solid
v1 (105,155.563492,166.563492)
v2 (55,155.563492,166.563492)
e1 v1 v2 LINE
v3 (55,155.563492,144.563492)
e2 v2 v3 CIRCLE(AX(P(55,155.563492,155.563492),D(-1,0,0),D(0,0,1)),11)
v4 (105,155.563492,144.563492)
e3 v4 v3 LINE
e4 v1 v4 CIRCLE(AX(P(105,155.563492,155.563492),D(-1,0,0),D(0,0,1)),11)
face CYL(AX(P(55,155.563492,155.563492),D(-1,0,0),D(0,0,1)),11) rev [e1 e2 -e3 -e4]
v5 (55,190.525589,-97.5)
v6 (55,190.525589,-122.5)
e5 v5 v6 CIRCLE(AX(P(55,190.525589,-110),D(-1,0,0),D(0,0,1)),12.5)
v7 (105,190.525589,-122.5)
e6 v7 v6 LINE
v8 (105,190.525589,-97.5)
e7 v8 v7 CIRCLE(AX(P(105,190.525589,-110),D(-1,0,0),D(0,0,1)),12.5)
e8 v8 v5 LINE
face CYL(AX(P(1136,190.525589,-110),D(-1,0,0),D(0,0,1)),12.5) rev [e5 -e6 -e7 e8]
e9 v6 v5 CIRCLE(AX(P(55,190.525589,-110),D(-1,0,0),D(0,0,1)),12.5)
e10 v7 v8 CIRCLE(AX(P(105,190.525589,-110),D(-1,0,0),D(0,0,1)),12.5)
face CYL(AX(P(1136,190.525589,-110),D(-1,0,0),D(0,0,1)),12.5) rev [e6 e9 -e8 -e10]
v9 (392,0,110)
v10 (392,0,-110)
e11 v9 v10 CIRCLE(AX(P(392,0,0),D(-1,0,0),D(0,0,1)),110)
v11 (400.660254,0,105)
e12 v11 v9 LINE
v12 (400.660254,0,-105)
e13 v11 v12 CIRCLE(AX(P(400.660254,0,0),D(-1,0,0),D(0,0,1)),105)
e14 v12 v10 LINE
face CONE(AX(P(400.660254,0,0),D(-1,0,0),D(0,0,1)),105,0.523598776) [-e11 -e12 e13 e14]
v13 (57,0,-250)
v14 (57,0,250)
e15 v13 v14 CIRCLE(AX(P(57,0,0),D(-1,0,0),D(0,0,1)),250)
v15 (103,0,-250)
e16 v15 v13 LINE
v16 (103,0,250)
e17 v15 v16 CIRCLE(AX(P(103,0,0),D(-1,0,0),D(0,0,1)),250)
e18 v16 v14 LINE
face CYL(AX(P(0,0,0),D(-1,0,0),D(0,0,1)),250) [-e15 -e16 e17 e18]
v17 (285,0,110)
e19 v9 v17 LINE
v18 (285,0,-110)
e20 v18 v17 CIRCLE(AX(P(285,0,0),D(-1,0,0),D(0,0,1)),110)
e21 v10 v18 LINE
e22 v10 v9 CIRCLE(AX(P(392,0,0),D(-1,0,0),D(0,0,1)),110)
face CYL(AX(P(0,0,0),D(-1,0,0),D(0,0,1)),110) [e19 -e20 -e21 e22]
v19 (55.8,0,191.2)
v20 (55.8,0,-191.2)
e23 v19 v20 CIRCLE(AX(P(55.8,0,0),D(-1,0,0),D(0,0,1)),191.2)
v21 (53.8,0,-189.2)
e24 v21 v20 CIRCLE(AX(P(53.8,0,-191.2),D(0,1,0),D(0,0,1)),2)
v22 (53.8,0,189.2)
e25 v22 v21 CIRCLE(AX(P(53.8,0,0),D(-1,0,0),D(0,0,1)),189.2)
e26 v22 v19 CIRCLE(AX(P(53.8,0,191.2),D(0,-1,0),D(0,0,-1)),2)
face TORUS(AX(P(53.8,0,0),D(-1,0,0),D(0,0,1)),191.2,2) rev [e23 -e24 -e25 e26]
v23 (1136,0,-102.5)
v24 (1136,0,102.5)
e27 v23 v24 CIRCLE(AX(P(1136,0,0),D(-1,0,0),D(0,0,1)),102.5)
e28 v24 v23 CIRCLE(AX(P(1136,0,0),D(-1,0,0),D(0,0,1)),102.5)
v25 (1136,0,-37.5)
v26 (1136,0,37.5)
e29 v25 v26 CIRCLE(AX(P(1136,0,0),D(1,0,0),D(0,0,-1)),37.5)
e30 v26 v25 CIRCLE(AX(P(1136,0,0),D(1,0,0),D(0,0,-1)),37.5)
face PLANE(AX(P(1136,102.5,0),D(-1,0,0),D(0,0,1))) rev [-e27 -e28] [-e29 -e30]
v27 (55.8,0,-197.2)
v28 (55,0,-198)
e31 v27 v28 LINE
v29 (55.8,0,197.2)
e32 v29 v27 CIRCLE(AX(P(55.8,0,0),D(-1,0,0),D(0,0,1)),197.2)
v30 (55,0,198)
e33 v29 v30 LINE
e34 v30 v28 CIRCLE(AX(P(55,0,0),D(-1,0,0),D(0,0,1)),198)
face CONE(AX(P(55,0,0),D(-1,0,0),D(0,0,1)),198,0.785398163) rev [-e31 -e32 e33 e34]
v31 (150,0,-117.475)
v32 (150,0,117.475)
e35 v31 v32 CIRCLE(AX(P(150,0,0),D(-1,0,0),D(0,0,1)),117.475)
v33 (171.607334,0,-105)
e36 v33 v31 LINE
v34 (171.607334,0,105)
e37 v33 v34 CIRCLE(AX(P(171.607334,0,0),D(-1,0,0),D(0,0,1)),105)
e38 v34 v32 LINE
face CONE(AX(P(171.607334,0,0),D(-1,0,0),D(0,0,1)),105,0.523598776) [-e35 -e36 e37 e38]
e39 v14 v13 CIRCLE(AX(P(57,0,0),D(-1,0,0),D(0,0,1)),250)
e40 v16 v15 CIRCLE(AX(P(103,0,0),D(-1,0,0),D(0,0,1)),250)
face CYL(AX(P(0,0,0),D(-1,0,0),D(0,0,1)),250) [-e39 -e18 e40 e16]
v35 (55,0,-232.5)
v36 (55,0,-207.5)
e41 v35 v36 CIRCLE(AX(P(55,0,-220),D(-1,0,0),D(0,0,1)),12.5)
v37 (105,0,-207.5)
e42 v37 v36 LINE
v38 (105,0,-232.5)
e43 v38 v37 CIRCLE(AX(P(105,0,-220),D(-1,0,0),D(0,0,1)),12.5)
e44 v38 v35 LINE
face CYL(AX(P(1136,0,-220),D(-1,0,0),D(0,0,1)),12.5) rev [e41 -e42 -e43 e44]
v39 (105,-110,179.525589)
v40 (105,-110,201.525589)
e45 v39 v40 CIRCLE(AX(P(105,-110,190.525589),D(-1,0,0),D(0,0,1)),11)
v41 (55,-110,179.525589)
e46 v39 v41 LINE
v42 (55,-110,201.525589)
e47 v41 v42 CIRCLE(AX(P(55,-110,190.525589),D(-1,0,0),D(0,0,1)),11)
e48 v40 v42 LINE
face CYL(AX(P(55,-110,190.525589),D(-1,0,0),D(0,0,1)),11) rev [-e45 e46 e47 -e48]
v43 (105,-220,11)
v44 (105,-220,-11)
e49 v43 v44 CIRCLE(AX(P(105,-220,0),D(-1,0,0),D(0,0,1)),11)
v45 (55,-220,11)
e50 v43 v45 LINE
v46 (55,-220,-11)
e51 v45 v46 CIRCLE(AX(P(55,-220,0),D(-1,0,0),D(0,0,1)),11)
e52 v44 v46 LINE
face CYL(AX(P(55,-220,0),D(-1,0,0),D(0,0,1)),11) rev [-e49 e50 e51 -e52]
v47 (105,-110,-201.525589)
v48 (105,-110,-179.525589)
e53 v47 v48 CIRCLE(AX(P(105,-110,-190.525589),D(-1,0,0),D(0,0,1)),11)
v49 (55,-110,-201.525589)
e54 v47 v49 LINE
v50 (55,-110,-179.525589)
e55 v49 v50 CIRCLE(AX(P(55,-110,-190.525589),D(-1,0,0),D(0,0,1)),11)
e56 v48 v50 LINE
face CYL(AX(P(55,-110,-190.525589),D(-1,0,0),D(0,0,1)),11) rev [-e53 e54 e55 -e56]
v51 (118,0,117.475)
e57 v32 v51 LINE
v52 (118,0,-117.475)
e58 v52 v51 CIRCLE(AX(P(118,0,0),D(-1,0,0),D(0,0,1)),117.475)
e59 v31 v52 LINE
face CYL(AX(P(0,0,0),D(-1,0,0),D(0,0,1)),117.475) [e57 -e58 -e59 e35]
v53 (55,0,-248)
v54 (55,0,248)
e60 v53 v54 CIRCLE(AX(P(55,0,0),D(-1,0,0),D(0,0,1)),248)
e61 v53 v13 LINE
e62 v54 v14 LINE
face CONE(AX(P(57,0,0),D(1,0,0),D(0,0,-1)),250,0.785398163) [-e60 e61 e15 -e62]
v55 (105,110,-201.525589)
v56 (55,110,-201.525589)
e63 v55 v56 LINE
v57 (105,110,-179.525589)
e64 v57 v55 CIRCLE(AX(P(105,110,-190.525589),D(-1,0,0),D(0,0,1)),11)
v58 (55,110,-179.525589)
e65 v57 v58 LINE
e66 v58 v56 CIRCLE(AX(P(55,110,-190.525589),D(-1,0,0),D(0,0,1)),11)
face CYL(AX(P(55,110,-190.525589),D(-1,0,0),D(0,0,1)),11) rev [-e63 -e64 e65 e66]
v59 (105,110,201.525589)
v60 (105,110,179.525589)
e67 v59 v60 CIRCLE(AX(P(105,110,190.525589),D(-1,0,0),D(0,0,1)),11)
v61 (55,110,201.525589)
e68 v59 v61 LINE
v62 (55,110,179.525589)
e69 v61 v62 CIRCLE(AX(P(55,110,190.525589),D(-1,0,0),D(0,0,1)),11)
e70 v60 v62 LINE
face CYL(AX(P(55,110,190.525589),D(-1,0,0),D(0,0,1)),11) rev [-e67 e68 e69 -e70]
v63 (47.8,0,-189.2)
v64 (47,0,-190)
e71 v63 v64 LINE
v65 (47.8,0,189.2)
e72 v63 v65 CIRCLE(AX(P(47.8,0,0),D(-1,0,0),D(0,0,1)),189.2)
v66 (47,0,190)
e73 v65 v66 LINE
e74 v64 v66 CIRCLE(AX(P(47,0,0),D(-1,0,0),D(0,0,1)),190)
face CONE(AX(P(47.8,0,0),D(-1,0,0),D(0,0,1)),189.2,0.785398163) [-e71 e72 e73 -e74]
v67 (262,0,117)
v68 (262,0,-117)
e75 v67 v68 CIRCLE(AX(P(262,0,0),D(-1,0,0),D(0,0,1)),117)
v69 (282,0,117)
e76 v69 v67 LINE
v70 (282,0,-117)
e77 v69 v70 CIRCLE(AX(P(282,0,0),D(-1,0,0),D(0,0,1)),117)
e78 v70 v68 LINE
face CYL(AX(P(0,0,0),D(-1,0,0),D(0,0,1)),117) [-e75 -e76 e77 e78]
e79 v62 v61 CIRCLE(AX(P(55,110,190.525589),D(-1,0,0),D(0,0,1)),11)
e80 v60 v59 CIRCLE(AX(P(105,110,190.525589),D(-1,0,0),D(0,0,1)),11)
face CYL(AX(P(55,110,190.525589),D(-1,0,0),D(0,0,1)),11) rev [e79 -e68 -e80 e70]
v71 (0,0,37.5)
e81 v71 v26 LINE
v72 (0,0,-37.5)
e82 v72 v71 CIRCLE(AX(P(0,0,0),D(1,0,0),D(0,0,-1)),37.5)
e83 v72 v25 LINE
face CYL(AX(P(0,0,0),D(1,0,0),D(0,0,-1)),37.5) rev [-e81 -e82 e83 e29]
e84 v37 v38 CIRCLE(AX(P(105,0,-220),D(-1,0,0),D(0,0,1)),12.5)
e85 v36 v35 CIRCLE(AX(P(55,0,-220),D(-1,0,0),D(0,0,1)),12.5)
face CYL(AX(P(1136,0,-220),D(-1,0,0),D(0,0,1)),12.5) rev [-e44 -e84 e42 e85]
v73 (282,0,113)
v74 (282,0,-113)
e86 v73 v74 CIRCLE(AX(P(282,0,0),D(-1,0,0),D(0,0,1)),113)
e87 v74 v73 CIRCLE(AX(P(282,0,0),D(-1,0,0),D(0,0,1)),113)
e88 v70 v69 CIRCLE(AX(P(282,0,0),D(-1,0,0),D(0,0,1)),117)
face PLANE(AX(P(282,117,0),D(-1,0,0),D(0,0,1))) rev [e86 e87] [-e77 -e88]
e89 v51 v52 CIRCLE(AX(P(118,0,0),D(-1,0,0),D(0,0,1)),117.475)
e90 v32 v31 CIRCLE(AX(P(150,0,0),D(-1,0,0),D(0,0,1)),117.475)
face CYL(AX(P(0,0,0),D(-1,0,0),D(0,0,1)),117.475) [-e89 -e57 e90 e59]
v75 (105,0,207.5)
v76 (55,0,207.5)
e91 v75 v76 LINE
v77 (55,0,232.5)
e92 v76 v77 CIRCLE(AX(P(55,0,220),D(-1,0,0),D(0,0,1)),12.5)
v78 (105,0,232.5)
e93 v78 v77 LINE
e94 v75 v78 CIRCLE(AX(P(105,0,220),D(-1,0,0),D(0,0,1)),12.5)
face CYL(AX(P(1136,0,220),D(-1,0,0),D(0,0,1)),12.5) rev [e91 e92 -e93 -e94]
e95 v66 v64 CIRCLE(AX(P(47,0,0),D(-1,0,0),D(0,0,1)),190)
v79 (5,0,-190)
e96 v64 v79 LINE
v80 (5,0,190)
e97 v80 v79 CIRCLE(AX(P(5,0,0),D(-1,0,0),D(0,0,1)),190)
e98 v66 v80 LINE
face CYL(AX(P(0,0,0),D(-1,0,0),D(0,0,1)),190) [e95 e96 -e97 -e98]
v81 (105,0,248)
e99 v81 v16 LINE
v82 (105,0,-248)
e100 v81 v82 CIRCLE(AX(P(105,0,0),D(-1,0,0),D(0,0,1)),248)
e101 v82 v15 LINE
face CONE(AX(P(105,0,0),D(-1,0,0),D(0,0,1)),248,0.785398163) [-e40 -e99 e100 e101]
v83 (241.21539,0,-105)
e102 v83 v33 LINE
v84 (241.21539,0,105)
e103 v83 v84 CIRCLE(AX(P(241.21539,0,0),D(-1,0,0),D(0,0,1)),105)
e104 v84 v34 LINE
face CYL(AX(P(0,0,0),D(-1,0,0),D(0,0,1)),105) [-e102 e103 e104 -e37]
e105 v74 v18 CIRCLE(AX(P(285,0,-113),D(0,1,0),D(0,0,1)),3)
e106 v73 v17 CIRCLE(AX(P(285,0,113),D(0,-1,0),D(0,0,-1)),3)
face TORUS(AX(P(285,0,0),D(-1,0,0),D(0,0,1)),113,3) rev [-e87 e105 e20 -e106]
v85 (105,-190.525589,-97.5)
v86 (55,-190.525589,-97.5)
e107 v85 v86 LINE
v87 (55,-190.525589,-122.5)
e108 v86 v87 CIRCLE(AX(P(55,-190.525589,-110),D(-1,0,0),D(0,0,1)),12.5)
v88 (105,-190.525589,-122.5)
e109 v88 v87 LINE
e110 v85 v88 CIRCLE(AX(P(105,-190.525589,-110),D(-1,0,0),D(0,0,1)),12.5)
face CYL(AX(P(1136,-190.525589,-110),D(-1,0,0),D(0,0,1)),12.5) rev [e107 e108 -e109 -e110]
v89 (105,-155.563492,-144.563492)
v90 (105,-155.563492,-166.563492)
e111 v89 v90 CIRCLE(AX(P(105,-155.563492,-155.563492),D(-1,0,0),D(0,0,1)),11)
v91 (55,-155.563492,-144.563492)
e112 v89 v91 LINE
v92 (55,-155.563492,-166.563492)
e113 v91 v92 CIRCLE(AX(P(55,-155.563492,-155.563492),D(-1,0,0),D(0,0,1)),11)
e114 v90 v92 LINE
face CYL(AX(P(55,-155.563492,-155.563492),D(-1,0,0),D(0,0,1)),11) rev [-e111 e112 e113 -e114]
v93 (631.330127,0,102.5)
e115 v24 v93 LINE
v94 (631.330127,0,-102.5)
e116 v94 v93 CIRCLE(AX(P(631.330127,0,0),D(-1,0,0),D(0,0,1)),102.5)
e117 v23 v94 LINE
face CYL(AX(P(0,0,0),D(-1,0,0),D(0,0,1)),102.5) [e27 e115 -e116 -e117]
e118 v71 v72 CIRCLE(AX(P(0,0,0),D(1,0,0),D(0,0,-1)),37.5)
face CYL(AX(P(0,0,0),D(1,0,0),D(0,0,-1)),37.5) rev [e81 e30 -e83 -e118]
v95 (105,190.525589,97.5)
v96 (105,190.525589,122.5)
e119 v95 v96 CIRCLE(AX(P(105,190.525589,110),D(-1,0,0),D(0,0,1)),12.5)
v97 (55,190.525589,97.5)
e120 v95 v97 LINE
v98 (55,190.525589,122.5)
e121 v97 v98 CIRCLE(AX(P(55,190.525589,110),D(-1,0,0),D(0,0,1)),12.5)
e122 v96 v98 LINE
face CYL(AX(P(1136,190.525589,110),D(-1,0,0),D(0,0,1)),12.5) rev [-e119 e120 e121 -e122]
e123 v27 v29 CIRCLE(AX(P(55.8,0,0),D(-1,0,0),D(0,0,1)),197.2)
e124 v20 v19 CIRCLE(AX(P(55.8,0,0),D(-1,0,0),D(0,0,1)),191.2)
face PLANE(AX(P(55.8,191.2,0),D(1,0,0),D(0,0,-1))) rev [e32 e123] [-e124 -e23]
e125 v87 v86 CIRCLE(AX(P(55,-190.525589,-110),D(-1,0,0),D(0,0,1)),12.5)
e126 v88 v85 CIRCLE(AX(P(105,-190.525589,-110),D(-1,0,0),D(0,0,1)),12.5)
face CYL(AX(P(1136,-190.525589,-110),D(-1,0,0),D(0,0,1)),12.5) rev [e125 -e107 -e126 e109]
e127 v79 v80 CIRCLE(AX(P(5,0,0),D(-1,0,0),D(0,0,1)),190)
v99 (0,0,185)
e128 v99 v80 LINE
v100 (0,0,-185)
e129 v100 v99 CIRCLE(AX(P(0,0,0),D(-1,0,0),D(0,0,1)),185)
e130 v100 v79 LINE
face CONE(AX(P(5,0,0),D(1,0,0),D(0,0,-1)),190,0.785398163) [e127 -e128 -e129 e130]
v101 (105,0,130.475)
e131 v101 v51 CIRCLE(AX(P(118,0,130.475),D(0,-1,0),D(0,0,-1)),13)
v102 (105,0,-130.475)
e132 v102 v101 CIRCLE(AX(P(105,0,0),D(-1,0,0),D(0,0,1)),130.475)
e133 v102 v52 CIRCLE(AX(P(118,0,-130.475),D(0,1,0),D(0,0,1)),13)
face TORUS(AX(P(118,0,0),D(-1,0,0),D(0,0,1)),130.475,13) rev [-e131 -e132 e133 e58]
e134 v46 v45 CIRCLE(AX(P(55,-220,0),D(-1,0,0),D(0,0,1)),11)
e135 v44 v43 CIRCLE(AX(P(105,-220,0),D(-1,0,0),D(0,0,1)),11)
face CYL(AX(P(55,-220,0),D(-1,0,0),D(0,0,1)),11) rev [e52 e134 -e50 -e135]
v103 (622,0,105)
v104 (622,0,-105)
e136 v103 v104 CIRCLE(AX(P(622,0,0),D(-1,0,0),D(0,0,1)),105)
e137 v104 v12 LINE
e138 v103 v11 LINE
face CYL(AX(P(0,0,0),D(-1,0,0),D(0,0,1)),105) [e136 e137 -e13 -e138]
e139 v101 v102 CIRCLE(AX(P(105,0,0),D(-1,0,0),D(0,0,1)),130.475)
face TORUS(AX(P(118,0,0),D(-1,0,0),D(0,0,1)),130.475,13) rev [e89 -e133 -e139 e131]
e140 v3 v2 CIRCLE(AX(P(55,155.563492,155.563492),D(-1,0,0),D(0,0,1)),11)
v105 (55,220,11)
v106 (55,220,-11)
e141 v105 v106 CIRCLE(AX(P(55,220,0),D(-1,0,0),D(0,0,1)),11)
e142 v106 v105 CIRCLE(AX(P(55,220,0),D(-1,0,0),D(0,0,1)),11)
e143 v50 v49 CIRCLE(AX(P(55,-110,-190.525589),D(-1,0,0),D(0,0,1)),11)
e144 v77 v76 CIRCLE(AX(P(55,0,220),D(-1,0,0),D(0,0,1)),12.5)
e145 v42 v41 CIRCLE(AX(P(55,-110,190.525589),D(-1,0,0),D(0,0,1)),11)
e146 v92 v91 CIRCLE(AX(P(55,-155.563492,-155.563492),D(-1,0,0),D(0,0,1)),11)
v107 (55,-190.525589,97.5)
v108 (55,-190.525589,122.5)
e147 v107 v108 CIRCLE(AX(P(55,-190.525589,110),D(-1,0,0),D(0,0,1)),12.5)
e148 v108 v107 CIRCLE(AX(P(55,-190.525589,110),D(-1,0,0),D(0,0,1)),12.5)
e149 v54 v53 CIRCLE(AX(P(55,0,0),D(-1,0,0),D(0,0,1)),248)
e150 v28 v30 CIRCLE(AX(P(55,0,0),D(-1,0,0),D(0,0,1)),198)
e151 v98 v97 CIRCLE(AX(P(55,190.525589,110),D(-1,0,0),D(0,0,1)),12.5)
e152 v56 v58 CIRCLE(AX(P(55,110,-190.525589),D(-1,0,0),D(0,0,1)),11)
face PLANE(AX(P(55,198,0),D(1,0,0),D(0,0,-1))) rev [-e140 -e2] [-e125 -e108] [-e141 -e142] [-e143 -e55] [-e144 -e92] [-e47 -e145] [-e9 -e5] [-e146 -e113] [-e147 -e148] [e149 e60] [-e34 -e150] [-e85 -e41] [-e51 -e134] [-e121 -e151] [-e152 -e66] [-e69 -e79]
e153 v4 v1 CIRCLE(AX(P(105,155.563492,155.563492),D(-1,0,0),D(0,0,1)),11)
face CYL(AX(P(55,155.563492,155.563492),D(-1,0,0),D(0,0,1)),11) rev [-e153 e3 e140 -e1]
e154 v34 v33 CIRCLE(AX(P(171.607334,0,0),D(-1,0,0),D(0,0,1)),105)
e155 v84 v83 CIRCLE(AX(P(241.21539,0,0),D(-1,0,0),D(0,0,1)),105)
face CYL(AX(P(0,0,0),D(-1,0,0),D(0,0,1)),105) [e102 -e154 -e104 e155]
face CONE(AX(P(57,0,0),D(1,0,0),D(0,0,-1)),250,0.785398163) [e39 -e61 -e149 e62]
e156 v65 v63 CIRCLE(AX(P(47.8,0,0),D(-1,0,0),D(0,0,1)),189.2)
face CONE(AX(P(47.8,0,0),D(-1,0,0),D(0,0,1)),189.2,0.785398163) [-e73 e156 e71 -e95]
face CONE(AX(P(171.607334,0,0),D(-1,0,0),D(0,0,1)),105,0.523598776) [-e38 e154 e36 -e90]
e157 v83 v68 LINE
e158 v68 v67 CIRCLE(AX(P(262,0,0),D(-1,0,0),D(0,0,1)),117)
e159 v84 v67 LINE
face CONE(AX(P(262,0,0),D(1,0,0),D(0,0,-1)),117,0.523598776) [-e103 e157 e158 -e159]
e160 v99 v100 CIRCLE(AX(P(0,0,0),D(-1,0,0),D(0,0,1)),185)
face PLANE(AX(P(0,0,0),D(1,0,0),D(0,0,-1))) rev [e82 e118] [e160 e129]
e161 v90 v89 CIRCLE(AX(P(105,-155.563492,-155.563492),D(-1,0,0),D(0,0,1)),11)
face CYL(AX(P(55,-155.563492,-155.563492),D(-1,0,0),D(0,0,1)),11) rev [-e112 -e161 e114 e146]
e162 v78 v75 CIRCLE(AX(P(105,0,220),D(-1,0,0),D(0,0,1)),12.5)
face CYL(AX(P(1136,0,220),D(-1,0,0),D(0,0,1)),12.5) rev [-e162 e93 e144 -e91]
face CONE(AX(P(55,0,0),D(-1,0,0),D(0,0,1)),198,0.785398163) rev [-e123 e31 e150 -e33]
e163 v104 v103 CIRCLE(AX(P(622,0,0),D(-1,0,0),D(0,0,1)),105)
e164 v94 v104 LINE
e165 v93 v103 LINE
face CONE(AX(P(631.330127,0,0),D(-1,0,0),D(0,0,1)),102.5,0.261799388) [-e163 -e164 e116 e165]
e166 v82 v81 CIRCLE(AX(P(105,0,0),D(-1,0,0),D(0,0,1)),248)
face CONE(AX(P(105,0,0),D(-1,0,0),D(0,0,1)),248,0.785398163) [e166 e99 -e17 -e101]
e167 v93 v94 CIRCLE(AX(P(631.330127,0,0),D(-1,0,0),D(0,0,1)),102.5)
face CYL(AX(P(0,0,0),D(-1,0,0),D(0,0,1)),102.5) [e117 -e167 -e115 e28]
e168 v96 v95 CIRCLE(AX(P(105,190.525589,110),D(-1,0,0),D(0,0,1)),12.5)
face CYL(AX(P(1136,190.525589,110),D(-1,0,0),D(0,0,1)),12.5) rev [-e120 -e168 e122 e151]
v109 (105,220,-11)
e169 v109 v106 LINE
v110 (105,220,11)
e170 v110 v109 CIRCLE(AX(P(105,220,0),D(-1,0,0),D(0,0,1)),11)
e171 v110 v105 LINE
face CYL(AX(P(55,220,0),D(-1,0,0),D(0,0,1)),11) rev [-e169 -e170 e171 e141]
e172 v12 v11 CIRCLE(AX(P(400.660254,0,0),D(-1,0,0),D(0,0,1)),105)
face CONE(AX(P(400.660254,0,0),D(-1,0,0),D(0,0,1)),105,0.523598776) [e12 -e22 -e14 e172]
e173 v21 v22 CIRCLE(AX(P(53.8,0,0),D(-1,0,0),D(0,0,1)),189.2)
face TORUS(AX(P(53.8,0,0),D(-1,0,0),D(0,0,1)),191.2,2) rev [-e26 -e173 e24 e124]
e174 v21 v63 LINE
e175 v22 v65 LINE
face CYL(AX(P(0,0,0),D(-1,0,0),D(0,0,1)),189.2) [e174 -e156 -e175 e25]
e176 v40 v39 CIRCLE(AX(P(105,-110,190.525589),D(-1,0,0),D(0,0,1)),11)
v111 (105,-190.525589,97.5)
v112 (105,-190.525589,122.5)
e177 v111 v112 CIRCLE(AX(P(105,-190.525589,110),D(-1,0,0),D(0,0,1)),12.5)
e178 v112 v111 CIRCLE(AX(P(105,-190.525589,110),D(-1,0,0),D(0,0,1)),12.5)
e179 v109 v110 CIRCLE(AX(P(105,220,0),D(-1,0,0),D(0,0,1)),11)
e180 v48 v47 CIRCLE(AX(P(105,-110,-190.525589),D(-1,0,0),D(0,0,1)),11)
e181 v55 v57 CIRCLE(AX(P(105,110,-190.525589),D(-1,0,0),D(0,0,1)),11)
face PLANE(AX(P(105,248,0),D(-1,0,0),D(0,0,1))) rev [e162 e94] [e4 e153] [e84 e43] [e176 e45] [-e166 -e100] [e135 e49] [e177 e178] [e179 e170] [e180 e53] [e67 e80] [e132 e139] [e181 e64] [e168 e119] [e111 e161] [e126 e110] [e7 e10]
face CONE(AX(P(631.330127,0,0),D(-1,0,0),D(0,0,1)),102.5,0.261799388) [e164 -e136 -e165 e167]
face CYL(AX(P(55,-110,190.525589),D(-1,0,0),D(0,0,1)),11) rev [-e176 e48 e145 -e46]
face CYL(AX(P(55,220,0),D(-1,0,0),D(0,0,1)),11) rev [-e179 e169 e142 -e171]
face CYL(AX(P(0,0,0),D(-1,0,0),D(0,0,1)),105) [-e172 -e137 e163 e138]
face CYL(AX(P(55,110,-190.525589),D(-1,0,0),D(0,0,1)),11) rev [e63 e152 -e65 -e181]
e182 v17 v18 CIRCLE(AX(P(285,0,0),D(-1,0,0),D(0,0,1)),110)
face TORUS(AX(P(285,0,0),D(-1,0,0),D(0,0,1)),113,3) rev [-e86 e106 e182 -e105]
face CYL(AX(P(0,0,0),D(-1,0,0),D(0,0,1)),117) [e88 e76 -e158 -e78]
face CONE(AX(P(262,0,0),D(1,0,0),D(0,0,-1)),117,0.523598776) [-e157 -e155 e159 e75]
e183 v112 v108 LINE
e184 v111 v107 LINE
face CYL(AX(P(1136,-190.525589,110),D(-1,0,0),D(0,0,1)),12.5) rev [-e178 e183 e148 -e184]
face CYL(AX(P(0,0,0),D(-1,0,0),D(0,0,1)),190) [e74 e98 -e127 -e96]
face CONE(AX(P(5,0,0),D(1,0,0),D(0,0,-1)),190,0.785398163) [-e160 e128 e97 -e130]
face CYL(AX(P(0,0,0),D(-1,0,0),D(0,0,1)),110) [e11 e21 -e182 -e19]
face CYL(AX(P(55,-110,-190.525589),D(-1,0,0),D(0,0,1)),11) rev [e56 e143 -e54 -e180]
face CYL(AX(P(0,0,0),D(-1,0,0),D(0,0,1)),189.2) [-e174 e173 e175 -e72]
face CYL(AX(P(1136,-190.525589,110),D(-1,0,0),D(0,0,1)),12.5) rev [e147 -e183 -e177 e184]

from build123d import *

# Parameters (mm, degrees)
M24X2_0_TAPPED_HOLE1_D = 22
SKETCH2_R              = 12.5
CUT_EXTRUDE1_DEPTH     = 1138.348231634
SKETCH4_R              = 37.5
CUT_EXTRUDE2_DEPTH     = 1190.746191421


with BuildPart() as part:
    # Sketch1 → Revolve1 (revolve)
    with BuildSketch(Plane.XY, mode=Mode.PRIVATE) as revolve1_sk:
        with BuildLine():
            Line((0, 0), (0, 185))
            Line((0, 185), (5, 190))
            Line((5, 190), (47, 190))
            Line((47, 190), (47.8, 189.2))
            Line((47.8, 189.2), (53.8, 189.2))
            ThreePointArc((53.8, 189.2), (55.214213562, 189.785786438), (55.8, 191.2))
            Line((55.8, 191.2), (55.8, 197.2))
            Line((55.8, 197.2), (55, 198))
            Line((55, 198), (55, 248))
            Line((55, 248), (57, 250))
            Line((57, 250), (103, 250))
            Line((103, 250), (105, 248))
            Line((105, 248), (105, 130.475))
            ThreePointArc((105, 130.475), (108.807611845, 121.282611845), (118, 117.475))
            Line((118, 117.475), (150, 117.475))
            Line((150, 117.475), (171.607333824, 105))
            Line((171.607333824, 105), (241.215390309, 105))
            Line((241.215390309, 105), (262, 117))
            Line((262, 117), (282, 117))
            Line((282, 117), (282, 113))
            ThreePointArc((282, 113), (282.878679656, 110.878679656), (285, 110))
            Line((285, 110), (392, 110))
            Line((392, 110), (400.660254038, 105))
            Line((400.660254038, 105), (622, 105))
            Line((622, 105), (631.330127019, 102.5))
            Line((631.330127019, 102.5), (1136, 102.5))
            Line((1136, 102.5), (1136, 0))
            Line((1136, 0), (0, 0))
        make_face()
    revolve(revolve1_sk.sketch.rotate(Axis((0, 0, 0), (1, 0, 0)), 90), axis=Axis((0, 0, 0), (1, 0, 0)))

    # M24x2.0 Tapped Hole1 (through all)
    with Locations(Plane(origin=(55, 220, 0), x_dir=(0, 0, -1), z_dir=(-1, 0, 0))):
        with Locations((0, 0), (-190.525588833, 110), (190.525588833, 110), (190.525588833, 330), (0, 440), (-190.525588833, 330), (-155.563491861, 64.436508139), (155.563491861, 375.563491861)):
            Hole(M24X2_0_TAPPED_HOLE1_D / 2)

    # Sketch2 → Cut-Extrude1 (cut, through all)
    with BuildSketch(Plane.ZY.offset(-55)):
        with Locations((-110, 190.525588833)):
            Circle(SKETCH2_R)
        with Locations((110, 190.525588833)):
            Circle(SKETCH2_R)
        with Locations((220, 0)):
            Circle(SKETCH2_R)
        with Locations((110, -190.525588833)):
            Circle(SKETCH2_R)
        with Locations((-110, -190.525588833)):
            Circle(SKETCH2_R)
        with Locations((-220, 0)):
            Circle(SKETCH2_R)
    extrude(amount=-CUT_EXTRUDE1_DEPTH, mode=Mode.SUBTRACT)

    # Sketch4 → Cut-Extrude2 (cut, through all)
    with BuildSketch(Plane(origin=(1136, 0, 0), x_dir=(0, 0, -1), z_dir=(1, 0, 0))):
        Circle(SKETCH4_R)
    extrude(amount=-CUT_EXTRUDE2_DEPTH, mode=Mode.SUBTRACT)


solid = part.part
